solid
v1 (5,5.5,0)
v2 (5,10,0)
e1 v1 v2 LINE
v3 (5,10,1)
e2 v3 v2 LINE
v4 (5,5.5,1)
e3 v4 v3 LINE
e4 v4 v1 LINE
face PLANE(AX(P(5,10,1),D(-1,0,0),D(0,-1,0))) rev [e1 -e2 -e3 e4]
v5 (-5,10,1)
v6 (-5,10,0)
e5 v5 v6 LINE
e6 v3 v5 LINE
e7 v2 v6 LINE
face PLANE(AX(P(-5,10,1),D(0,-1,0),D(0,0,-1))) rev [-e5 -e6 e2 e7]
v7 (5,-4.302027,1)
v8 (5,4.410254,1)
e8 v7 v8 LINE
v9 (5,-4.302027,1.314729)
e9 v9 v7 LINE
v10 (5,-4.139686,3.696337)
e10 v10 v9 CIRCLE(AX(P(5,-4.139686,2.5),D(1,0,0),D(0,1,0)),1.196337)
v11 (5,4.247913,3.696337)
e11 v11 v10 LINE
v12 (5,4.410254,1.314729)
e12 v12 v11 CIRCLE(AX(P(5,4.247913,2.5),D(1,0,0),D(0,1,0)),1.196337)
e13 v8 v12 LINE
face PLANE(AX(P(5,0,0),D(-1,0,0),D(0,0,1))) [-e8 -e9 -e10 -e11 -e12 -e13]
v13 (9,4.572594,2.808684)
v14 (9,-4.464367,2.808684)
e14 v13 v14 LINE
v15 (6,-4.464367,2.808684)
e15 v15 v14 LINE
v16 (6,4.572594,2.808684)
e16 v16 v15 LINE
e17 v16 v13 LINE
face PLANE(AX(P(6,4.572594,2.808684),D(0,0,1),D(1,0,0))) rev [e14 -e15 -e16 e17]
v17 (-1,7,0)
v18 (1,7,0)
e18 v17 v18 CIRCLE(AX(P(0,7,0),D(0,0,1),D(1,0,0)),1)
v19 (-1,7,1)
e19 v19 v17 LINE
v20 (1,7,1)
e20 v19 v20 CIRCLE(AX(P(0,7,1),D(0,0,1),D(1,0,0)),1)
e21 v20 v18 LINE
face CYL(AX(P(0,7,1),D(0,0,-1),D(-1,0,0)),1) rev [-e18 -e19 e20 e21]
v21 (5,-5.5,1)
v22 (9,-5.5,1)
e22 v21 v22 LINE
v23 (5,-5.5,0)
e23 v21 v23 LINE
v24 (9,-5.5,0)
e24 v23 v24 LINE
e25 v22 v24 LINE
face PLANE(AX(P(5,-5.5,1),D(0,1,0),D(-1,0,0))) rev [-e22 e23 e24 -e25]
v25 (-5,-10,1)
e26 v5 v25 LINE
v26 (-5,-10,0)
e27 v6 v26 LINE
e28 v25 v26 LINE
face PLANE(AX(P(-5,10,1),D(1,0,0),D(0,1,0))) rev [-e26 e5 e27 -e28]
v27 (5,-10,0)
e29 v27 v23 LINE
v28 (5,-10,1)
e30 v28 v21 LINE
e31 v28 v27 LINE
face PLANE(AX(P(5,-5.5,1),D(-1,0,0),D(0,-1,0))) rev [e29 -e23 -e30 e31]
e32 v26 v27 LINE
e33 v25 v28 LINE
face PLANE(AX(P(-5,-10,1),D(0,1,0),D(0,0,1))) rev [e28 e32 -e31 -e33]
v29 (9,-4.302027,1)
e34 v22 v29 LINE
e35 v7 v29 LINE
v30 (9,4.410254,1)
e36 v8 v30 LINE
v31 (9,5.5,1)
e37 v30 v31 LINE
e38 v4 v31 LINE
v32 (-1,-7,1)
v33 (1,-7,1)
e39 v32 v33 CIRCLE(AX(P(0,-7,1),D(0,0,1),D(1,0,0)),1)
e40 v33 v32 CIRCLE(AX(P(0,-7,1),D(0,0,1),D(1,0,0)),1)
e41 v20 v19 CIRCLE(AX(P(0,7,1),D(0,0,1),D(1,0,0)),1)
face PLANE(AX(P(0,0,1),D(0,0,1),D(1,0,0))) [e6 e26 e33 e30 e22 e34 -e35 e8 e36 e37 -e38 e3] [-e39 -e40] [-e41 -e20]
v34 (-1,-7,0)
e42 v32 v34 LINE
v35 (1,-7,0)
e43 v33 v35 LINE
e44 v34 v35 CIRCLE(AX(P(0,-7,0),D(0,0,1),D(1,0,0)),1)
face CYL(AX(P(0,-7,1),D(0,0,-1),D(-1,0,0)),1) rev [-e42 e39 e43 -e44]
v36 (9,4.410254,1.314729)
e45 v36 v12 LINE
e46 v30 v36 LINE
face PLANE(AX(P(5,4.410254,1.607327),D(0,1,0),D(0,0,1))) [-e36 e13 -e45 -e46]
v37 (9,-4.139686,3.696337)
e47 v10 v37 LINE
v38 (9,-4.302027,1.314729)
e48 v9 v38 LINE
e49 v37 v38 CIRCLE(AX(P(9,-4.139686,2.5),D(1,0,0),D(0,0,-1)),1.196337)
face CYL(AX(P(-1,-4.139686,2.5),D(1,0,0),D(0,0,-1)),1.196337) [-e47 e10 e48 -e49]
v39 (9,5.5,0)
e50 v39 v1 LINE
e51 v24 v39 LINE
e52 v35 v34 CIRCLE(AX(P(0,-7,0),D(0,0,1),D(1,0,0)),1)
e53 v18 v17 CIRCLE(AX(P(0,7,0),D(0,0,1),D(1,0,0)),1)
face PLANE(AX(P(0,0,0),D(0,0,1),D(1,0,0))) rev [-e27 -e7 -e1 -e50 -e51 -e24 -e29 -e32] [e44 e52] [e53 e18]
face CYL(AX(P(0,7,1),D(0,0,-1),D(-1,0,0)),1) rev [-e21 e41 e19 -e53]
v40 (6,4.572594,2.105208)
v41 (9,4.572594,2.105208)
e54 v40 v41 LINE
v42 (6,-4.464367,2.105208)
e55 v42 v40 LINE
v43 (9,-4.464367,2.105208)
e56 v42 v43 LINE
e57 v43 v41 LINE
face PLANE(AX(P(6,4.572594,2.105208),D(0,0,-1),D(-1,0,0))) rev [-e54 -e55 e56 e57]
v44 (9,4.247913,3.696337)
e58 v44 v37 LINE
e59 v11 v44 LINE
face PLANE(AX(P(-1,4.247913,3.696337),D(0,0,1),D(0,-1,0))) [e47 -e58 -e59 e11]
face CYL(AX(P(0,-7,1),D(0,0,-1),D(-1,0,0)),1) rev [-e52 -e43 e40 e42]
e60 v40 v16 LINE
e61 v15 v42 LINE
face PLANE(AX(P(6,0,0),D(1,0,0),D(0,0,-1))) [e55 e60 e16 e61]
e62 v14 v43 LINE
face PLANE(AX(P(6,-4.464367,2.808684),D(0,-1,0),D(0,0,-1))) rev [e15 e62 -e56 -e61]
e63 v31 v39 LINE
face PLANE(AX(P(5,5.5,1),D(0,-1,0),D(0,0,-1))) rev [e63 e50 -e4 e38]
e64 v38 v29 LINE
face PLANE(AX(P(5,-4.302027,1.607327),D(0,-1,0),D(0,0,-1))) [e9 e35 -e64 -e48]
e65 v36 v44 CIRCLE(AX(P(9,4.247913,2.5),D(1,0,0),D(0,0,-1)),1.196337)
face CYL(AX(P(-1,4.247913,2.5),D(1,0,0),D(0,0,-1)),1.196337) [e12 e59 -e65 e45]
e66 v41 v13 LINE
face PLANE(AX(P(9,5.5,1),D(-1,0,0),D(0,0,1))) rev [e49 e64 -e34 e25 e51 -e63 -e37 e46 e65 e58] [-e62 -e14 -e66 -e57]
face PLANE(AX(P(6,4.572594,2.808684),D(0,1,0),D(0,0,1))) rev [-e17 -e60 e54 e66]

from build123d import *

# Parameters (mm, degrees)
SKETCH1_R           = 1
BOSS_EXTRUDE1_DEPTH = 1
SKETCH2_W           = 4
SKETCH2_H           = 11
BOSS_EXTRUDE2_DEPTH = 3
SKETCH3_W           = 3
SKETCH3_H           = 11
CUT_EXTRUDE1_DEPTH  = 10
SKETCH4_W           = 0.703476056
SKETCH4_H           = 9.036961638
CUT_EXTRUDE2_DEPTH  = 3
SKETCH5_W           = 0.607326988
SKETCH5_H           = 8.712280381
BOSS_EXTRUDE3_DEPTH = 4


with BuildPart() as part:
    # Sketch1 → Boss-Extrude1 (new body)
    with BuildSketch(Plane.XY):
        Polygon((-5, 10), (5, 10), (5, 5.5), (9, 5.5), (9, -5.5), (5, -5.5), (5, -10), (-5, -10), align=None)
        with Locations((0, 7)):
            Circle(SKETCH1_R, mode=Mode.SUBTRACT)
        with Locations((0, -7)):
            Circle(SKETCH1_R, mode=Mode.SUBTRACT)
    extrude(amount=BOSS_EXTRUDE1_DEPTH)

    # Sketch2 → Boss-Extrude2 (add)
    with BuildSketch(Plane.XY.offset(1)):
        with Locations((7, 0)):
            Rectangle(SKETCH2_W, SKETCH2_H)
    extrude(amount=BOSS_EXTRUDE2_DEPTH)

    # Sketch3 → Cut-Extrude1 (cut)
    with BuildSketch(Plane(origin=(9, 0, 0), x_dir=(0, 0, -1), z_dir=(1, 0, 0))):
        with Locations((-2.5, 0)):
            Rectangle(SKETCH3_W, SKETCH3_H)
        with BuildLine():
            Line((-1.303663494, 4.247913105), (-1.303663494, -4.13968602))
            ThreePointArc((-1.303663494, -4.13968602), (-2.5, -5.336022526), (-3.696336506, -4.13968602))
            Line((-3.696336506, -4.13968602), (-3.696336506, 4.247913105))
            ThreePointArc((-3.696336506, 4.247913105), (-2.5, 5.444249611), (-1.303663494, 4.247913105))
        make_face(mode=Mode.SUBTRACT)
    extrude(amount=-CUT_EXTRUDE1_DEPTH, mode=Mode.SUBTRACT)


with BuildPart() as cut_extrude1_piece_1:
    # of the separate pieces the step leaves, piece 1, a body of its own (cut_extrude1_pieces)
    add(part.part.solids().sort_by_distance((-5, 10, 0))[0])



with BuildPart() as cut_extrude1_piece_2:
    # of the separate pieces the step leaves, piece 2, a body of its own (cut_extrude1_pieces)
    add(part.part.solids().sort_by_distance((9, 4.247913105, 3.696336506))[0])

    # Sketch4 → Cut-Extrude2 (cut)
    with BuildSketch(Plane(origin=(9, 0, 0), x_dir=(0, 0, -1), z_dir=(1, 0, 0))):
        with Locations((-2.456945609, 0.054113543)):
            Rectangle(SKETCH4_W, SKETCH4_H)
    extrude(amount=-CUT_EXTRUDE2_DEPTH, mode=Mode.SUBTRACT)


with BuildPart() as cut_extrude1_piece_1_1:
    add(cut_extrude1_piece_1.part)

    add(cut_extrude1_piece_2.part)  # Boss-Extrude3 merges Cut-Extrude1 piece 2
    # Sketch5 → Boss-Extrude3 (add)
    with BuildSketch(Plane(origin=(9, 0, 0), x_dir=(0, 0, -1), z_dir=(1, 0, 0))):
        with Locations((-1.303663494, 0.054113543)):
            Rectangle(SKETCH5_W, SKETCH5_H)
    extrude(amount=-BOSS_EXTRUDE3_DEPTH)


solid = cut_extrude1_piece_1_1.part
